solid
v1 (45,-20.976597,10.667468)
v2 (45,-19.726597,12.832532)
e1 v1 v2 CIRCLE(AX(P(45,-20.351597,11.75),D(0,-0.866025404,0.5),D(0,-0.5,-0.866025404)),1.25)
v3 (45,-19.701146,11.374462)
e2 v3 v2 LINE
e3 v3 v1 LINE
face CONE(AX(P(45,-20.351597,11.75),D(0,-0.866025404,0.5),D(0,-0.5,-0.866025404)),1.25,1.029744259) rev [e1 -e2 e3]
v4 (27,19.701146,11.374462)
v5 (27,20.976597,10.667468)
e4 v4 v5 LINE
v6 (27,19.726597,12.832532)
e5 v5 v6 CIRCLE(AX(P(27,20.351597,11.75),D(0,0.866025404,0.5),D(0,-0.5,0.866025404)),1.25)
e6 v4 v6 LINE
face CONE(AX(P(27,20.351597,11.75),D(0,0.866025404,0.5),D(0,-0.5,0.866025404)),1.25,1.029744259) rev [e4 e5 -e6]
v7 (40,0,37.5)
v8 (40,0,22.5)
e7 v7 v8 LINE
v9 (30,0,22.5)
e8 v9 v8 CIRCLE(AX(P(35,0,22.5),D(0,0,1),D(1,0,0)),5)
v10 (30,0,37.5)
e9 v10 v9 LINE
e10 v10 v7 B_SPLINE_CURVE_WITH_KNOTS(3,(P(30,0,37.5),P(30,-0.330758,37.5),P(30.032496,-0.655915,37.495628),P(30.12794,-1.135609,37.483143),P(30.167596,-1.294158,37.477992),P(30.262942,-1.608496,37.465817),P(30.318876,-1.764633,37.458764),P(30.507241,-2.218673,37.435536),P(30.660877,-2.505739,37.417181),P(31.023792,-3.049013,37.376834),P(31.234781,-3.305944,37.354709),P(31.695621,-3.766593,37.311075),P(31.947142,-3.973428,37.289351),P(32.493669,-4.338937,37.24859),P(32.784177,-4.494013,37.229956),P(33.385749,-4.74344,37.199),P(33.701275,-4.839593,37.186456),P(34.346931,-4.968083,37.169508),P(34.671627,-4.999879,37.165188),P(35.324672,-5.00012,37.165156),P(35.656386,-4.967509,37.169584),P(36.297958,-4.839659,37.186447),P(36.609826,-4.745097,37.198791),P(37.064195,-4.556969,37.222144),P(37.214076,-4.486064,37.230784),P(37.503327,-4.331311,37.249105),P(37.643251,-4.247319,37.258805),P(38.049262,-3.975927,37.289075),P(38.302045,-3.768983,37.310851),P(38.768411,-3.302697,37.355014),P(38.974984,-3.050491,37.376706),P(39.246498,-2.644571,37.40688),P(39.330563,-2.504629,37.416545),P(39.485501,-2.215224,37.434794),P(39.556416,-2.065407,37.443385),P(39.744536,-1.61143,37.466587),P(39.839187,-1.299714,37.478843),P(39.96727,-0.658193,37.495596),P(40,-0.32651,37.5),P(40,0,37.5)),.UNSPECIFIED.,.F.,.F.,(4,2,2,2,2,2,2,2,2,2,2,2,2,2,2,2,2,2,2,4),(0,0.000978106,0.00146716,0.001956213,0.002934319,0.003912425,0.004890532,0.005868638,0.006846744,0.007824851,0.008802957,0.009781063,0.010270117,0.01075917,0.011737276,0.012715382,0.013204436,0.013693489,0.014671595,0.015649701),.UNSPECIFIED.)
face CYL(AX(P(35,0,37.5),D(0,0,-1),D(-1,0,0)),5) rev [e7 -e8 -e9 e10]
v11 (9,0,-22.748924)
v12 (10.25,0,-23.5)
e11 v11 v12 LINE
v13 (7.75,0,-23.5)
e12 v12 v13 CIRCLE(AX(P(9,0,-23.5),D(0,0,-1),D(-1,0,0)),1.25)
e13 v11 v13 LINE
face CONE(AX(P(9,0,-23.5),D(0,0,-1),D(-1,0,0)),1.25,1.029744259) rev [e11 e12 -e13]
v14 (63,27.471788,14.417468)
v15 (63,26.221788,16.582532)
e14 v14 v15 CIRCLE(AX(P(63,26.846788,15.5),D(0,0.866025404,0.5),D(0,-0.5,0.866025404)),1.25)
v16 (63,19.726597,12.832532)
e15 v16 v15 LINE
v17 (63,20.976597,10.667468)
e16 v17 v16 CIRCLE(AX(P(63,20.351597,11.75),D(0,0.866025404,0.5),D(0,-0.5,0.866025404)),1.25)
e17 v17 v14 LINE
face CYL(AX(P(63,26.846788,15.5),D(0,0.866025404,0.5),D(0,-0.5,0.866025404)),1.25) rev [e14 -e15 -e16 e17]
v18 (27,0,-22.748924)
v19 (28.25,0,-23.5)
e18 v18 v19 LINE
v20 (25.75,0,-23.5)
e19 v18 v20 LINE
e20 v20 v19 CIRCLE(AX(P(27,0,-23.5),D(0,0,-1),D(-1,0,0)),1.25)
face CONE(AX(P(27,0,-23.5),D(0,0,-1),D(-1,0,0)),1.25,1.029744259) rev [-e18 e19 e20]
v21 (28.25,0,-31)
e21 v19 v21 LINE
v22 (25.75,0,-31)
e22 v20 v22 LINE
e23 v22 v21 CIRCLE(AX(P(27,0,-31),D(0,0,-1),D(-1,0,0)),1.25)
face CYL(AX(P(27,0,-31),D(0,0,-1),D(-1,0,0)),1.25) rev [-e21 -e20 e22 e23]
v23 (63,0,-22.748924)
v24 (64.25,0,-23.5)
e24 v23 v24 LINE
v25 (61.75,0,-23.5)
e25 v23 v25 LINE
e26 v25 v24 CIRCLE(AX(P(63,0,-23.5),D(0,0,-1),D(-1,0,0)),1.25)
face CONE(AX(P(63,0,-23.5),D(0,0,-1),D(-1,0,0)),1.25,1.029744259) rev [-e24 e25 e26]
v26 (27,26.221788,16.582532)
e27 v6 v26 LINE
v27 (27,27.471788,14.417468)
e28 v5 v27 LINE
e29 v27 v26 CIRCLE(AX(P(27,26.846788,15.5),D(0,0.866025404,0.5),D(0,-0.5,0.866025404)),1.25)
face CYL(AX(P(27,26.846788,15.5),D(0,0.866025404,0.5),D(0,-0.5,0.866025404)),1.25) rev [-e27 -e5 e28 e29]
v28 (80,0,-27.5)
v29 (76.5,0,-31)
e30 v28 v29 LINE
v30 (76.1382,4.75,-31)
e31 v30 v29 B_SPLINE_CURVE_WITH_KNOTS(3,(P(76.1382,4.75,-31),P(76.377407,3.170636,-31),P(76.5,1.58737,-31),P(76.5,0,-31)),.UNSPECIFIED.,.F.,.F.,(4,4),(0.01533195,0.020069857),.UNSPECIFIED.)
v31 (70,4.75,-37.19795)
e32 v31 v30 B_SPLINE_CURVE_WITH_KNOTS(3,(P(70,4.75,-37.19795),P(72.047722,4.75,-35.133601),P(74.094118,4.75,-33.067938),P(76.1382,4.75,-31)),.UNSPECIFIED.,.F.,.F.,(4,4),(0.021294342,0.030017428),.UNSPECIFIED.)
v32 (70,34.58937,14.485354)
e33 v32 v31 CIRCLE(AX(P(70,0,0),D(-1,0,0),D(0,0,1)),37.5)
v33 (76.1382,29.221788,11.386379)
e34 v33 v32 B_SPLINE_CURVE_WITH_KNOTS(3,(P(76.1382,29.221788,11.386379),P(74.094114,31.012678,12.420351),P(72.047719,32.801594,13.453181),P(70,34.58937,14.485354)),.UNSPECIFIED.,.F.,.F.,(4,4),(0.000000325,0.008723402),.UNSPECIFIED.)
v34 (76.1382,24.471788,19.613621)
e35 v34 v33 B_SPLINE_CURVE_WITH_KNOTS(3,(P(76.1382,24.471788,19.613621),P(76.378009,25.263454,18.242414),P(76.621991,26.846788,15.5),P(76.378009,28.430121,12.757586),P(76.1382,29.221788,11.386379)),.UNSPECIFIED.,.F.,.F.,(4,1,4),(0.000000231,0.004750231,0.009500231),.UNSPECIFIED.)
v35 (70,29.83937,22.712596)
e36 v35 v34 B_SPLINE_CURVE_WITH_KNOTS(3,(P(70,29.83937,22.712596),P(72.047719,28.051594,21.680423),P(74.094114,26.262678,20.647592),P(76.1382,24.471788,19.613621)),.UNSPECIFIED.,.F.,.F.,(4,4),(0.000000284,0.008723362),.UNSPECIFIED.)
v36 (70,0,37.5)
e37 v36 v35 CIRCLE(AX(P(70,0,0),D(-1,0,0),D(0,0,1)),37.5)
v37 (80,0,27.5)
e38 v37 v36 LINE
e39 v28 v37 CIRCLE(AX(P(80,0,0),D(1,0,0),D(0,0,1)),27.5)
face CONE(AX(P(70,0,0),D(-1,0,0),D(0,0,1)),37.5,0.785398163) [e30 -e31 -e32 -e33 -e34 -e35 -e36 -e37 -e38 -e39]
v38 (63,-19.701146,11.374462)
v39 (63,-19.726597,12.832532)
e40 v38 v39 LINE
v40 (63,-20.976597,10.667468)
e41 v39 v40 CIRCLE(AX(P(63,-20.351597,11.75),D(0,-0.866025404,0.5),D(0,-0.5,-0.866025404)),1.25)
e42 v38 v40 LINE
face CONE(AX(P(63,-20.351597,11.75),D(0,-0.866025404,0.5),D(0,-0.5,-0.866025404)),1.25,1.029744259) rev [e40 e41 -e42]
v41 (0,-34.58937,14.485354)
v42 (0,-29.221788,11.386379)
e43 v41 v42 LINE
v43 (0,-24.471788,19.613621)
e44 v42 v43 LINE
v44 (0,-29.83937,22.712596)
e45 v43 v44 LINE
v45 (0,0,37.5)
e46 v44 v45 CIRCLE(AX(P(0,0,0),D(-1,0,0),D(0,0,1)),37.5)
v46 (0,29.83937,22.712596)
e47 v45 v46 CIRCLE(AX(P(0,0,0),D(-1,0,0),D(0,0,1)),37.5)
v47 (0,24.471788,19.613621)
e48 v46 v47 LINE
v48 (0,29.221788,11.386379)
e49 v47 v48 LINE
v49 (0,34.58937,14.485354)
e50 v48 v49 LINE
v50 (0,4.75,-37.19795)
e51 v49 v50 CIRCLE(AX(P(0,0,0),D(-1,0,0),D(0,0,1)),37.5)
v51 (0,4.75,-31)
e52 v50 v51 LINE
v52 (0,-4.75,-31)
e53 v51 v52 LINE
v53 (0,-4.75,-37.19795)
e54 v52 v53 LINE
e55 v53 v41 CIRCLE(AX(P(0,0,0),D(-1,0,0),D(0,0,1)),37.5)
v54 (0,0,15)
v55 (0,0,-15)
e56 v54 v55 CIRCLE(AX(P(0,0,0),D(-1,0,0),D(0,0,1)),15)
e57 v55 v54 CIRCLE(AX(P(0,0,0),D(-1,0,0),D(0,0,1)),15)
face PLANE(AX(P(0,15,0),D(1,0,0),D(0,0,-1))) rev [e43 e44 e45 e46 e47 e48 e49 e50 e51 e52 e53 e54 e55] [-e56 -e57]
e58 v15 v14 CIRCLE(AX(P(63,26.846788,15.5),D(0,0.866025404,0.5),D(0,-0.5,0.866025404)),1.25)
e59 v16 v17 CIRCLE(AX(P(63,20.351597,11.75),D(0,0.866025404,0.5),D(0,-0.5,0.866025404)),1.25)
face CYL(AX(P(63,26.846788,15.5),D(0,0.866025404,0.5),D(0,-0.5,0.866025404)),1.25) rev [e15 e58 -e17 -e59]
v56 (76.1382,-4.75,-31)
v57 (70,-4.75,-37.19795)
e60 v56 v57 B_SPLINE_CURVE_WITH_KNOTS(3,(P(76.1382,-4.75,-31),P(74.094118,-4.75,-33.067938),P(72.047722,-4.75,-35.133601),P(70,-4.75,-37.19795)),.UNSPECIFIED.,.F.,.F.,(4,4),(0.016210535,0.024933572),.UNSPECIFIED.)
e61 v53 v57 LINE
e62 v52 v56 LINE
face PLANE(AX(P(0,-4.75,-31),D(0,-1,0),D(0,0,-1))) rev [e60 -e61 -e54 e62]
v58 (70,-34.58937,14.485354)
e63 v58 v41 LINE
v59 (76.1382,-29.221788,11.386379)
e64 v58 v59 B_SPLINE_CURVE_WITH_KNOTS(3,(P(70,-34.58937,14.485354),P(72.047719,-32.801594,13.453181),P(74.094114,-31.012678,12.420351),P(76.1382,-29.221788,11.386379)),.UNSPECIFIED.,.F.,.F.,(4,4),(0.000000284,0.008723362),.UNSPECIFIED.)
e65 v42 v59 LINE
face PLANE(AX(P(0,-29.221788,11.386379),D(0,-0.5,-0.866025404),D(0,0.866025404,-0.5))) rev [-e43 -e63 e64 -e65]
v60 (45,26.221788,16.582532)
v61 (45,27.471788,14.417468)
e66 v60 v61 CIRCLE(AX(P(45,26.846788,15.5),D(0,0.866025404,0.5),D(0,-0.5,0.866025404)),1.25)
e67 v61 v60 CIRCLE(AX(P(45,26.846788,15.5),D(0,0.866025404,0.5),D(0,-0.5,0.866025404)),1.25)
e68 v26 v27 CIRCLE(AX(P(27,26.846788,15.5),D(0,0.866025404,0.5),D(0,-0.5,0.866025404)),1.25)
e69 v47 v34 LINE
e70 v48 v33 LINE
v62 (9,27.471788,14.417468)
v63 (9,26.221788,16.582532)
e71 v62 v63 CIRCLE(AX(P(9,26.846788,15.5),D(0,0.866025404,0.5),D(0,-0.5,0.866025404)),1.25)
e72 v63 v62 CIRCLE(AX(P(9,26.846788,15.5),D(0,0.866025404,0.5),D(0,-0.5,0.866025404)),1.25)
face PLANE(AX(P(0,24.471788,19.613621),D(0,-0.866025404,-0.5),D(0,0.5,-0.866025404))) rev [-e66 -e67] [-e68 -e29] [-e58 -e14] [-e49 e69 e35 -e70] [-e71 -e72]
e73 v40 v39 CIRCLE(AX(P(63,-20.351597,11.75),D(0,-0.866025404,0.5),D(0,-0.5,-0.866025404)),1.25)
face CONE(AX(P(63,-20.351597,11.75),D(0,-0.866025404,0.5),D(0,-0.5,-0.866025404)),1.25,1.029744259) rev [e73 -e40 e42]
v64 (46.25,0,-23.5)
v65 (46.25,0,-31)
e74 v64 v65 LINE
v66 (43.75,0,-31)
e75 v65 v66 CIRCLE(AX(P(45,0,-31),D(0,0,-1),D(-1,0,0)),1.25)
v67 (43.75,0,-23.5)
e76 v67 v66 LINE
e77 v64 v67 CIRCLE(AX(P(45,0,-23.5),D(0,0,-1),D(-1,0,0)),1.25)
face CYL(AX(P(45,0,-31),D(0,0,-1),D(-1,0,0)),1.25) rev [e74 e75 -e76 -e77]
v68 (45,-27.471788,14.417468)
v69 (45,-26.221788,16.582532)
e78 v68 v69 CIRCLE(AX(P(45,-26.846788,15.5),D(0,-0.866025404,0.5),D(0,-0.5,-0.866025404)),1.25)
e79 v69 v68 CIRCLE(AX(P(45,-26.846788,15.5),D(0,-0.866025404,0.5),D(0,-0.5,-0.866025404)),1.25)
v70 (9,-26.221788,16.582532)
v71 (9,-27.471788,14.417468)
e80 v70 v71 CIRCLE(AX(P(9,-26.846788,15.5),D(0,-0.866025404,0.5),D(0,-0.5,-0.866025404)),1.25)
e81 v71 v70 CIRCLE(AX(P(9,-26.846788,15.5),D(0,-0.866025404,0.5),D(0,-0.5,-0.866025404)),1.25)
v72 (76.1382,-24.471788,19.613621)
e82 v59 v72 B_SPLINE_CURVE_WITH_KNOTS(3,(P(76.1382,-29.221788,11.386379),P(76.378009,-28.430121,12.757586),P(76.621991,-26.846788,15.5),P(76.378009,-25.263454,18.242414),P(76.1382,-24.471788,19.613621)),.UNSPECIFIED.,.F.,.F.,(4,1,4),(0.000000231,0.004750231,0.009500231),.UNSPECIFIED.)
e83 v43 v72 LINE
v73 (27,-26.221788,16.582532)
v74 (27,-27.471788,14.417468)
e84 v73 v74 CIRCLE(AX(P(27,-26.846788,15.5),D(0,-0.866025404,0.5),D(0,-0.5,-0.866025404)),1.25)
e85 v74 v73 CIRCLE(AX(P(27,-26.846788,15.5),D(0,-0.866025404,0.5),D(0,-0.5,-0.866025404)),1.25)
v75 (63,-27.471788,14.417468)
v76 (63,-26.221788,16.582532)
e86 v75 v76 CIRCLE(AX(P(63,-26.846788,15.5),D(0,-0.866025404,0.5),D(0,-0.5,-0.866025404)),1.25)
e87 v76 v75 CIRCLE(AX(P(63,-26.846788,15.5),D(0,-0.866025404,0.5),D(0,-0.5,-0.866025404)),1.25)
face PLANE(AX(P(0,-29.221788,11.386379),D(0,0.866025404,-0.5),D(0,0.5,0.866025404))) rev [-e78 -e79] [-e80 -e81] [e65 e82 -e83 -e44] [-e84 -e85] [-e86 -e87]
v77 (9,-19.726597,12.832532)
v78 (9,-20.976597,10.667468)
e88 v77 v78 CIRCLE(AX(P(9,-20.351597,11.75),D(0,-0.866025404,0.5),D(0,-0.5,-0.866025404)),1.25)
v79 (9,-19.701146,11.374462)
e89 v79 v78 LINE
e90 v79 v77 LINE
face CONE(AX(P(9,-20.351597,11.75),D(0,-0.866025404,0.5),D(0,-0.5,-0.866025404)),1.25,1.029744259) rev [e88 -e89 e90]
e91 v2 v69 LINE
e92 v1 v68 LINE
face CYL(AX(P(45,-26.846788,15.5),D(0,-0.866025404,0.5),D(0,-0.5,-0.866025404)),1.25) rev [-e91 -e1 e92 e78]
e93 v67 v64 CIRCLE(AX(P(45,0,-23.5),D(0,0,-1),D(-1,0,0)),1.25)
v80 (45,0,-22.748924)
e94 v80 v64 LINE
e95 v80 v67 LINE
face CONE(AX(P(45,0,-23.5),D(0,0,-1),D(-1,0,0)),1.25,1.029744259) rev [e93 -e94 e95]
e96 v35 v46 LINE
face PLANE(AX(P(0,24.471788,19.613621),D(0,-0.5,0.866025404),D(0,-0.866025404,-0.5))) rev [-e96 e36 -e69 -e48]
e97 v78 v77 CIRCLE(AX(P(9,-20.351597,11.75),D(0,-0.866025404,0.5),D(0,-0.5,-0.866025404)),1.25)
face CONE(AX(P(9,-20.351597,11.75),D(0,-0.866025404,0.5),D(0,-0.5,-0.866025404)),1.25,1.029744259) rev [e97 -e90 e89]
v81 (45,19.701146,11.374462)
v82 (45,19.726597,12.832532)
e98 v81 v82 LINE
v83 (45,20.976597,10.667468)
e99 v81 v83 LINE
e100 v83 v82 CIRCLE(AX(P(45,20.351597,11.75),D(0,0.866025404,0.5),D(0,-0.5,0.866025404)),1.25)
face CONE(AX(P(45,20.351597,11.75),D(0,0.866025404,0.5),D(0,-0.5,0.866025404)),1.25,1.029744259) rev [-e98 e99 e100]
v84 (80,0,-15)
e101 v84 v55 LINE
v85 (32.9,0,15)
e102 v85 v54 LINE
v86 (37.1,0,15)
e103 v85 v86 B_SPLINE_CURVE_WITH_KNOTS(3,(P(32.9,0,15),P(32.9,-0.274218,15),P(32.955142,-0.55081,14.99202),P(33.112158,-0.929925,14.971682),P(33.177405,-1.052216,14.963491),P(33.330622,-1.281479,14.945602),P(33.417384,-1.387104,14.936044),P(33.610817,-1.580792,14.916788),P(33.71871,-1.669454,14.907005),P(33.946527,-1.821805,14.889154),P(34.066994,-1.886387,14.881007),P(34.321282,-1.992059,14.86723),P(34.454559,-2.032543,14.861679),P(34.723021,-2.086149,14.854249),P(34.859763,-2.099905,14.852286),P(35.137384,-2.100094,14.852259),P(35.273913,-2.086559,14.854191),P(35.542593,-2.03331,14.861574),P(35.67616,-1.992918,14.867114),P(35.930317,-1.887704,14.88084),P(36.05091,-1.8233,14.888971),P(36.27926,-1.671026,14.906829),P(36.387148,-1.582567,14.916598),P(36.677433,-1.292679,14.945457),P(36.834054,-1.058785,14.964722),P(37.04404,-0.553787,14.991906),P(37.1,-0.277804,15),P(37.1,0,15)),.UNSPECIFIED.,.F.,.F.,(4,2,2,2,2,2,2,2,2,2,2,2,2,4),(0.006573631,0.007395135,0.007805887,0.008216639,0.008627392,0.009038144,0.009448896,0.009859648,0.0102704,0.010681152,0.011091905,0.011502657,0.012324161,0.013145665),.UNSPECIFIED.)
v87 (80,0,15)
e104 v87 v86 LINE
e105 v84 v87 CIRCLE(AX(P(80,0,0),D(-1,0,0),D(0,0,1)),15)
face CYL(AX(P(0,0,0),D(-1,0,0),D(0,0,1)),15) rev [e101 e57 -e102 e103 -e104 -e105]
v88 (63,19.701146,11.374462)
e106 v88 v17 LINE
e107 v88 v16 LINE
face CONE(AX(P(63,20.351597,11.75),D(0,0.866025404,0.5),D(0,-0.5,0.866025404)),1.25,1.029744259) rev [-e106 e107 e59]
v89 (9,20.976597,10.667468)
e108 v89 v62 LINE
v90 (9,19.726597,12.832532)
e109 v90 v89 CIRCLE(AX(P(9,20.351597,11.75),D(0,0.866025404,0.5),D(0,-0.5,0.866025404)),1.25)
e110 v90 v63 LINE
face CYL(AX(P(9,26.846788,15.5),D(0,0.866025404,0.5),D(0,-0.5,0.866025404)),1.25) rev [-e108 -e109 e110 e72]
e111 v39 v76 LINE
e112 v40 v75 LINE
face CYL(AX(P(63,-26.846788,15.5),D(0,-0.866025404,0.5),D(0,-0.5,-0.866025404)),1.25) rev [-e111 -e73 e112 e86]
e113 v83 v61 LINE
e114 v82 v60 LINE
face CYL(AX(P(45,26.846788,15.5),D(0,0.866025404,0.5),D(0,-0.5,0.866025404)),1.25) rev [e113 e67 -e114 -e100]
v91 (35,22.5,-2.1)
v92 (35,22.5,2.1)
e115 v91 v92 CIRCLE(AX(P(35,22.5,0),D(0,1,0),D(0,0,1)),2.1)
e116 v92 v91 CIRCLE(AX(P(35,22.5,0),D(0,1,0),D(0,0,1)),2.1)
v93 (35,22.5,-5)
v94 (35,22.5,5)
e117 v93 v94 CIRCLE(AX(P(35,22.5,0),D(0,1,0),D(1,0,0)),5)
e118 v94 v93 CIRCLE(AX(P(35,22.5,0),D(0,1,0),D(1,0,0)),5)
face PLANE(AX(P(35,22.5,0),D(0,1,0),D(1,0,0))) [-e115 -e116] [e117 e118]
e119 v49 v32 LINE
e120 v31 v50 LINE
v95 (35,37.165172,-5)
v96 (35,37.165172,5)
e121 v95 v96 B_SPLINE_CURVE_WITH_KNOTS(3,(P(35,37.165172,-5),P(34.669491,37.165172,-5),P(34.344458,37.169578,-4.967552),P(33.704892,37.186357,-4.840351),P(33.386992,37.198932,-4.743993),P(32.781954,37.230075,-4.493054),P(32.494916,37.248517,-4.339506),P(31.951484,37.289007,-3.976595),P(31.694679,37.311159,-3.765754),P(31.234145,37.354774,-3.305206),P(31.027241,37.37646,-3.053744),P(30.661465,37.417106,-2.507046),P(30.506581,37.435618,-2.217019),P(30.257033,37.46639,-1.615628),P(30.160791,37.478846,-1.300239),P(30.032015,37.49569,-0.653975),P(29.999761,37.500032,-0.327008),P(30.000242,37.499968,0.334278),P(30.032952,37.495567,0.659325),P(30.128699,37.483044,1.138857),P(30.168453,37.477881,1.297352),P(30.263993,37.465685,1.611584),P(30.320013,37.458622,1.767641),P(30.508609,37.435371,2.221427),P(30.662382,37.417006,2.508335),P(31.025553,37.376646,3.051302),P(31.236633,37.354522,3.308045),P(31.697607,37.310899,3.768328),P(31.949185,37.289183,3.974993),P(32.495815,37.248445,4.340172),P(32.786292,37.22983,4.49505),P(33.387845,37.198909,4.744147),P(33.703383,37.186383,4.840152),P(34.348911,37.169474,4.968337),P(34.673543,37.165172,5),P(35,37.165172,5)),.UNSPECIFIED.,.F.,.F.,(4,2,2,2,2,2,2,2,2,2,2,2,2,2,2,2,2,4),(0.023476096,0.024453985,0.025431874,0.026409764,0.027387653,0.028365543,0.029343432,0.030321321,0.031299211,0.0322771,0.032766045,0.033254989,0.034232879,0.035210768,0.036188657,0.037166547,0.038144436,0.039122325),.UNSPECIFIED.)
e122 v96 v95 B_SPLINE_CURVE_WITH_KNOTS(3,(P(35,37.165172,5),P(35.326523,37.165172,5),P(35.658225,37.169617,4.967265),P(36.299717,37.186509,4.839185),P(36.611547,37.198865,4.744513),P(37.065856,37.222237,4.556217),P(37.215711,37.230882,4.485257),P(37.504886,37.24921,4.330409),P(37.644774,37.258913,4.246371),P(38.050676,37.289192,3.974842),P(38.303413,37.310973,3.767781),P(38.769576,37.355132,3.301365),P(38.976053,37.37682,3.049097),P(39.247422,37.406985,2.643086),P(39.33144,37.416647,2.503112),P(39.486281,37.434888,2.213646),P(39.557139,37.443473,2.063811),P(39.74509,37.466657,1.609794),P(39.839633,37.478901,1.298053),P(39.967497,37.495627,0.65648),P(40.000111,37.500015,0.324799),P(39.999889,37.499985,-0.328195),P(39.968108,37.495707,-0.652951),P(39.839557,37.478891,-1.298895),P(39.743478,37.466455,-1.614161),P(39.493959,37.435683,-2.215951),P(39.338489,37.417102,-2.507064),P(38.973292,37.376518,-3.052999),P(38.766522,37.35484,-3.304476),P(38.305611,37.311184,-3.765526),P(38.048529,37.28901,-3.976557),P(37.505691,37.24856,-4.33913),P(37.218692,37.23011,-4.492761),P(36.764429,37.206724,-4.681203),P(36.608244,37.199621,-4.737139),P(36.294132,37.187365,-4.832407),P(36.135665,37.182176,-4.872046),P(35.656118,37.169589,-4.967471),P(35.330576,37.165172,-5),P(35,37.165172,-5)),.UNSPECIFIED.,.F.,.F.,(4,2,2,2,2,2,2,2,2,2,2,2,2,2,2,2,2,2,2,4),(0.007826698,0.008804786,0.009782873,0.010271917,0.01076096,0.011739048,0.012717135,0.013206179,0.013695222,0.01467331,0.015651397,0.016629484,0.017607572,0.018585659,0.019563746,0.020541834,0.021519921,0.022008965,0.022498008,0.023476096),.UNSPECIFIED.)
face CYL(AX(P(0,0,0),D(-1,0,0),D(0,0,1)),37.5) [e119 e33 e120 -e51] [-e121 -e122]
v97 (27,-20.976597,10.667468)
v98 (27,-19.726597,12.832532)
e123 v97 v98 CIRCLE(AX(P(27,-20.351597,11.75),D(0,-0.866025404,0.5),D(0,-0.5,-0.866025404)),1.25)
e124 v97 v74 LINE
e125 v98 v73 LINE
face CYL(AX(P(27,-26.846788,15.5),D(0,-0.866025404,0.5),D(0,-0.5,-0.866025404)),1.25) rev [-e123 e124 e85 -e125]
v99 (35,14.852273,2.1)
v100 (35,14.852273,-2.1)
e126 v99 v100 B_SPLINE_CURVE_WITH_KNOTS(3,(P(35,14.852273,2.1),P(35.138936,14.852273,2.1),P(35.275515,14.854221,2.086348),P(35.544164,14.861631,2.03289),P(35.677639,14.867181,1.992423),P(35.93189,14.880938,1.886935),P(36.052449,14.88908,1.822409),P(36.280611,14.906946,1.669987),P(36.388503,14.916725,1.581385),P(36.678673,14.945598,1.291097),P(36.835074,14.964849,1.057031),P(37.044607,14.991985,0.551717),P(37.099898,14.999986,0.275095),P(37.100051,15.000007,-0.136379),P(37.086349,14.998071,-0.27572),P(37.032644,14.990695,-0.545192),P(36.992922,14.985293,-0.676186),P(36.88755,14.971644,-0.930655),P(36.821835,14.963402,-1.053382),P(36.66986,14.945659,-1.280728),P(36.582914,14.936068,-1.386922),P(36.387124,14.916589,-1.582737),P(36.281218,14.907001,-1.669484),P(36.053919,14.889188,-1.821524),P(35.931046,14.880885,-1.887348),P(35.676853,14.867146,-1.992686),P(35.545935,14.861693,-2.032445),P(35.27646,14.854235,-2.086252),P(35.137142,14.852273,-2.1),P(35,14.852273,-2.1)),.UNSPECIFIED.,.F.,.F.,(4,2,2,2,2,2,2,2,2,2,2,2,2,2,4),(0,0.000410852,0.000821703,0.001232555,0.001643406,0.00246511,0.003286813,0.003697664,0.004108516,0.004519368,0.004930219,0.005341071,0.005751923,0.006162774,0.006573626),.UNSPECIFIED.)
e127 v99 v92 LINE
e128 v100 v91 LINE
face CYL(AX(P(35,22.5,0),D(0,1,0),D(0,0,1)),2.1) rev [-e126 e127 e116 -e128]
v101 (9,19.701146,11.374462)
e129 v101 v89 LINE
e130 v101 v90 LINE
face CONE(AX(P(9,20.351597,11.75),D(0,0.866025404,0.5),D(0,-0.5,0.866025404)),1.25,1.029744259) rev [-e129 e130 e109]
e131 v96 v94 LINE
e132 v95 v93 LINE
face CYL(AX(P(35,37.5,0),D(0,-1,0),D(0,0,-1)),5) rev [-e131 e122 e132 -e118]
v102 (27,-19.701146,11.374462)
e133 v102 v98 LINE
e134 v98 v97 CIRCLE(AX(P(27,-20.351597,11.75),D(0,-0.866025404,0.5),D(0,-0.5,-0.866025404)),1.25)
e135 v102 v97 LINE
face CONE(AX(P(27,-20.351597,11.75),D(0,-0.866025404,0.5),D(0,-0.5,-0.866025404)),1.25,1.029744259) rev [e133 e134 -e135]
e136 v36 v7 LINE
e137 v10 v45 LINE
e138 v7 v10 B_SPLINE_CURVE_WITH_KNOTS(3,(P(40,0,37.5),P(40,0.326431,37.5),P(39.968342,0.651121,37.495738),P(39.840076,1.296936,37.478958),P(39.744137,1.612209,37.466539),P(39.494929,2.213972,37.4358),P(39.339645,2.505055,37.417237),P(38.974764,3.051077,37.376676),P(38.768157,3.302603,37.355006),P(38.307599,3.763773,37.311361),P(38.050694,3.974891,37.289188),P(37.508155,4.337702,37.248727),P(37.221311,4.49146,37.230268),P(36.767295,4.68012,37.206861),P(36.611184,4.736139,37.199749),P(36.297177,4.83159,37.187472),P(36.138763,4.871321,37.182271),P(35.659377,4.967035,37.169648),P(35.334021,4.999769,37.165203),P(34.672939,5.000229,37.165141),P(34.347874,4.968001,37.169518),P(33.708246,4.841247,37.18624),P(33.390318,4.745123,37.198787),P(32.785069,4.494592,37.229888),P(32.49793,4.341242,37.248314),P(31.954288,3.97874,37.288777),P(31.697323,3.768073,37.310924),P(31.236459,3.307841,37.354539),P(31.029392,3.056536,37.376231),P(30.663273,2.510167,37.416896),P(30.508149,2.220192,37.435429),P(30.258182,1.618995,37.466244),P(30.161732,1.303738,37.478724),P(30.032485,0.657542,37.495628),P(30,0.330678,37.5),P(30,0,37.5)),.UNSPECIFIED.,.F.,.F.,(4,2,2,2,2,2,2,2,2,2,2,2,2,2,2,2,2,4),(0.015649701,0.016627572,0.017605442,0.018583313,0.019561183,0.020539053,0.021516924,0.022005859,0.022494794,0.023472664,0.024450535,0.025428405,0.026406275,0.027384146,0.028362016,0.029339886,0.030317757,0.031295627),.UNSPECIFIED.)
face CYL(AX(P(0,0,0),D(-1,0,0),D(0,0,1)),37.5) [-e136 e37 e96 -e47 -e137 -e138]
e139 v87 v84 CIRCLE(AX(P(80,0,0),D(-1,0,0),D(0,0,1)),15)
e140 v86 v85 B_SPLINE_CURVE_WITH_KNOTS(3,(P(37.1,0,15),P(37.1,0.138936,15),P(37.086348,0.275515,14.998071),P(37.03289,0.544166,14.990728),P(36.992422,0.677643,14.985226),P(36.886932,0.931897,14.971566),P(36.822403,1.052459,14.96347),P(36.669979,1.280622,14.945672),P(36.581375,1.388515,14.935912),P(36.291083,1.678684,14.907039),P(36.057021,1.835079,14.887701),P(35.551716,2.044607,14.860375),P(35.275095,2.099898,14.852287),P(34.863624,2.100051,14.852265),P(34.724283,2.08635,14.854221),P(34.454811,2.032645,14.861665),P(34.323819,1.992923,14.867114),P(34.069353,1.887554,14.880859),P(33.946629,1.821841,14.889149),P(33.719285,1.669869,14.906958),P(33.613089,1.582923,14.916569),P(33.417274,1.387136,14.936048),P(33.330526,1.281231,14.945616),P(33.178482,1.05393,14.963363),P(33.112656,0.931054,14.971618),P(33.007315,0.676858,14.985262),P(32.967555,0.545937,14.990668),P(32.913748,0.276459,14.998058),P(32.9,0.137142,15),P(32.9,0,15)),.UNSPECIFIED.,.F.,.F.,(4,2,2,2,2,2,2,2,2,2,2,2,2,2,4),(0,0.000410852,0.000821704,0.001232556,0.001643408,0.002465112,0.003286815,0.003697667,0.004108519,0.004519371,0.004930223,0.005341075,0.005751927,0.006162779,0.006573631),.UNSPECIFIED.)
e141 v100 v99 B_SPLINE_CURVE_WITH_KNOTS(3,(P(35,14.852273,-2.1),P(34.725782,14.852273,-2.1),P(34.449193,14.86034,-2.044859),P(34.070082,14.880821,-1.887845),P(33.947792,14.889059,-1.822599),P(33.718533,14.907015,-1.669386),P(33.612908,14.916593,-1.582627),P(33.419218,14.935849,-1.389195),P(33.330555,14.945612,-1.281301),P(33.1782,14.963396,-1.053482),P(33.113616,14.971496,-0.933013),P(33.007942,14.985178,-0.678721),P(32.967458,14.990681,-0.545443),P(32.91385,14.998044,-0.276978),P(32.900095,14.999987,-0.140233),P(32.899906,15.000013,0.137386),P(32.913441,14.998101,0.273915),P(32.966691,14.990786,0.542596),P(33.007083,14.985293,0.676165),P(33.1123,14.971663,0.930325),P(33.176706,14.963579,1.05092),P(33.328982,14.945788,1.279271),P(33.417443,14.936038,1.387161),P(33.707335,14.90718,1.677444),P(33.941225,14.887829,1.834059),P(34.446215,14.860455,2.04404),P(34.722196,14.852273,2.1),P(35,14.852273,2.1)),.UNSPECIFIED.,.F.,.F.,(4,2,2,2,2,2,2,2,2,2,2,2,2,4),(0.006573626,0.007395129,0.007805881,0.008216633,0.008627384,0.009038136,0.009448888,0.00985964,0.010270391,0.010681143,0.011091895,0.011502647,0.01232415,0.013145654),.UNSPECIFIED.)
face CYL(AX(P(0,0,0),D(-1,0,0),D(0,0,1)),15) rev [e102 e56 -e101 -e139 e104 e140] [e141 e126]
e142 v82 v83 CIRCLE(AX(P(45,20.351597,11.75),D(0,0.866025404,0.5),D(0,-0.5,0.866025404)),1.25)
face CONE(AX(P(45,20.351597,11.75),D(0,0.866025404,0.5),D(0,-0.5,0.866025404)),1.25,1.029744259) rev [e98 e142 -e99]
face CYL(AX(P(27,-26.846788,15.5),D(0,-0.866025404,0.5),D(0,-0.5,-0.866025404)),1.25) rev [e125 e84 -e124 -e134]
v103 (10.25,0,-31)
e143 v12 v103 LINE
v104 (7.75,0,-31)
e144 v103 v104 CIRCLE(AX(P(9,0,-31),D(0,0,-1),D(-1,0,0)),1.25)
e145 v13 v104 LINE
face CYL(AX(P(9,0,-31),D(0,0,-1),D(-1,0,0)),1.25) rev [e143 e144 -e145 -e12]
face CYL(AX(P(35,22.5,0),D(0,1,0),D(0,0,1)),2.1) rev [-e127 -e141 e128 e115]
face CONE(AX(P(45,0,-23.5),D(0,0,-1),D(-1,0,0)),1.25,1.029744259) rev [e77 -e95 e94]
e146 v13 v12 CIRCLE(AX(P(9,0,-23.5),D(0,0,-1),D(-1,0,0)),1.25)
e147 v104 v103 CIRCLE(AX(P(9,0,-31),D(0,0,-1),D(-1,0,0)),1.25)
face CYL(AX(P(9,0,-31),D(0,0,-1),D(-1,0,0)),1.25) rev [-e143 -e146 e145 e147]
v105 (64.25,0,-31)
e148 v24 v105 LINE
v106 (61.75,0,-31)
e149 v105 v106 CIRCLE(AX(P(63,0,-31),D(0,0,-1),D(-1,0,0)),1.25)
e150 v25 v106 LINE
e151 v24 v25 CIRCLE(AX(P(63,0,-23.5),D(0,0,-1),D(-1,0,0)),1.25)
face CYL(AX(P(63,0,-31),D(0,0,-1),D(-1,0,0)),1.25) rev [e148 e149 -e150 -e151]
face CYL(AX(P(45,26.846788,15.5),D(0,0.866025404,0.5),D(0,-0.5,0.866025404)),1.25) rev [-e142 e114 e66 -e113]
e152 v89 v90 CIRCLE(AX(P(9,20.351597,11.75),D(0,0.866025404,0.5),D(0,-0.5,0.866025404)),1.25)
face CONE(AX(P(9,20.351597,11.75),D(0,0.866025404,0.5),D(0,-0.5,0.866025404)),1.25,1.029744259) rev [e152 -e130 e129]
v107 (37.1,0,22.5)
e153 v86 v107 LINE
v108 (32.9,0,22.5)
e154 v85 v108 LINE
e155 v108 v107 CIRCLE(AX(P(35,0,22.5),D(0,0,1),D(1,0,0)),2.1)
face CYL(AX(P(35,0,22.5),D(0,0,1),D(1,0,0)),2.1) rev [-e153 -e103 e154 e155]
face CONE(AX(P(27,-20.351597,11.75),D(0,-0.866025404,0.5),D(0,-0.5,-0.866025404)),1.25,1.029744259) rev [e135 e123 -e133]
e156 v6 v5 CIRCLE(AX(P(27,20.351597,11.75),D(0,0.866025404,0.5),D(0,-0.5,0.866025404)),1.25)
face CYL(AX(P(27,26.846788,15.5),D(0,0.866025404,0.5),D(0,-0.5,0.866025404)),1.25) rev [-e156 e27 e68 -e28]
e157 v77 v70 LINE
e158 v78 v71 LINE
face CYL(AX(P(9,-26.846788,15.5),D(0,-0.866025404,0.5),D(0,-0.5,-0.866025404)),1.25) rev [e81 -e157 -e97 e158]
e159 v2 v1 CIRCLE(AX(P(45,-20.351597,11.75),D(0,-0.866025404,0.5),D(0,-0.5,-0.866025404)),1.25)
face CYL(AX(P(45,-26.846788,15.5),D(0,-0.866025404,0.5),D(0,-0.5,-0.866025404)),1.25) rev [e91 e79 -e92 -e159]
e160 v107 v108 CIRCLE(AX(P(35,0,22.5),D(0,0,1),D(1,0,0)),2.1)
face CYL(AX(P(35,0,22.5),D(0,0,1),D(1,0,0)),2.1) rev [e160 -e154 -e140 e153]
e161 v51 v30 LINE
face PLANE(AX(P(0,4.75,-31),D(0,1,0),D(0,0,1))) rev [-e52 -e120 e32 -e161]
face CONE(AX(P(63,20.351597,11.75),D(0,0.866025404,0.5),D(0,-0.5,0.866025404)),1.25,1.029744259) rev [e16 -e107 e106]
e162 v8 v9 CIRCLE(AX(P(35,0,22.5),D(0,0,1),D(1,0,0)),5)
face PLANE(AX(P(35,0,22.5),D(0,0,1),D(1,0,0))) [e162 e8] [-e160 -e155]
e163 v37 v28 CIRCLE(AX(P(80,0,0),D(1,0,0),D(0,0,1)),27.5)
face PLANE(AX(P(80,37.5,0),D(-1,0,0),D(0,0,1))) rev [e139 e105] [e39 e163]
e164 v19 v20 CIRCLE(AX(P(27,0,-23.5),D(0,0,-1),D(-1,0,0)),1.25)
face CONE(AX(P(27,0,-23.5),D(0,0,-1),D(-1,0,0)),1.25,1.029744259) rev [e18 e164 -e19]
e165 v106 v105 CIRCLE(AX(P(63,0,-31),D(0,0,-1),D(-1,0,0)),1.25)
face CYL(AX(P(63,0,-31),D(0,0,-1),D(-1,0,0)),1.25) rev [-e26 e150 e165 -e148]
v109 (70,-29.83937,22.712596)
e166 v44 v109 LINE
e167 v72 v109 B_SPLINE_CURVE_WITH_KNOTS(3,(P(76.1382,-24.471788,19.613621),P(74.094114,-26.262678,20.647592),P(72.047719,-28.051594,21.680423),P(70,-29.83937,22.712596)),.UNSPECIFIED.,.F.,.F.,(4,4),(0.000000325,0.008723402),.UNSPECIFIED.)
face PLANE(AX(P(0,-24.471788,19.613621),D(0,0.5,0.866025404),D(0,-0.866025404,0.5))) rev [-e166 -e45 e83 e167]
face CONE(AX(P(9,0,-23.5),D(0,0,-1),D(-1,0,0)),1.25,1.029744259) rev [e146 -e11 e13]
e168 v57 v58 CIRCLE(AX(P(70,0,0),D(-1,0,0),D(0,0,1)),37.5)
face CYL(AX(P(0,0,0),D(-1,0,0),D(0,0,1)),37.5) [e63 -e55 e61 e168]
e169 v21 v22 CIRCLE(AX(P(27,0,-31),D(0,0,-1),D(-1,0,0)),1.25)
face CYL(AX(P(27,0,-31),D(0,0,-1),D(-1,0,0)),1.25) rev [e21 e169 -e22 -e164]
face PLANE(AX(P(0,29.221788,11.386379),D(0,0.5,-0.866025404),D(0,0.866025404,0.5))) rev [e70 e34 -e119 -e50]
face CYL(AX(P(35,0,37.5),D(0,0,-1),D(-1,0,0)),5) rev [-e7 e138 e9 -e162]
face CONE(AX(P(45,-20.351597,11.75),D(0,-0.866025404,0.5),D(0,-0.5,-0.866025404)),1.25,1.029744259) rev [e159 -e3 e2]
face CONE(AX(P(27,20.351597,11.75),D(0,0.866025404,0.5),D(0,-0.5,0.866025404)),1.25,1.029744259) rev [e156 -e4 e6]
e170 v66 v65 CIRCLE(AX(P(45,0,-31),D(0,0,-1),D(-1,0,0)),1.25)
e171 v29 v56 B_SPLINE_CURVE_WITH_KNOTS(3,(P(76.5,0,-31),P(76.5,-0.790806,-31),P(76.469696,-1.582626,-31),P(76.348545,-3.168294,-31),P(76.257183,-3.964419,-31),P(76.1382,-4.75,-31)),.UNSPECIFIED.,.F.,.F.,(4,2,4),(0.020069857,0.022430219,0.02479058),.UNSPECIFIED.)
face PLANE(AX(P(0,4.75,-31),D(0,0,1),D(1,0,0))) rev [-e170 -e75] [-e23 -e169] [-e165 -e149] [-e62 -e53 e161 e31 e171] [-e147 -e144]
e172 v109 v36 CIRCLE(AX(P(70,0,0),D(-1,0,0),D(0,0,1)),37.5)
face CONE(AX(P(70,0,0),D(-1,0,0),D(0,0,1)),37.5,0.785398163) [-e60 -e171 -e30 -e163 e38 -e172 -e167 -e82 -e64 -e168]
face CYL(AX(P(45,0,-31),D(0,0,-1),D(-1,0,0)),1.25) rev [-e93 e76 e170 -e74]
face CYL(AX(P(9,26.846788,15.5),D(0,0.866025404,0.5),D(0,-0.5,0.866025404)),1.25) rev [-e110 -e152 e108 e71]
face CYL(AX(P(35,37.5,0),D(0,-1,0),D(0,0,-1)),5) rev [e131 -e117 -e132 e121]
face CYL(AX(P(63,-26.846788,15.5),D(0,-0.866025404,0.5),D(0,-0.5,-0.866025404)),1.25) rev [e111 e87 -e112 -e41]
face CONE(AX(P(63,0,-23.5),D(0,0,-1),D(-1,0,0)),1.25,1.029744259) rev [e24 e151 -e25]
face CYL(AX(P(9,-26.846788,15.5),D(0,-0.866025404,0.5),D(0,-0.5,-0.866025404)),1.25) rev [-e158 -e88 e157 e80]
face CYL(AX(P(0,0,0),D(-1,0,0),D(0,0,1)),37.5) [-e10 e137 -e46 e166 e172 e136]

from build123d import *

# Parameters (mm, degrees)
SKETCH1_W                  = 80
SKETCH1_H                  = 22.5
CHAMFER1_SIZE              = 10
CUT_EXTRUDE1_START         = 22.5
SKETCH2_R                  = 5
CUT_EXTRUDE1_DEPTH         = 74.481769102
CIRPATTERN1_COUNT          = 2
CIRPATTERN1_ANGLE          = 90
SKETCH5_W                  = 13
SKETCH5_H                  = 9.5
CUT_EXTRUDE2_DEPTH         = 96.981769264
M3_TAPPED_HOLE1_AT_2_COUNT = 2
M3_TAPPED_HOLE1_AT_2_PITCH = 18
M3_TAPPED_HOLE1_AT_3_COUNT = 2
M3_TAPPED_HOLE1_AT_3_PITCH = 18
M3_TAPPED_HOLE1_AT_4_COUNT = 2
M3_TAPPED_HOLE1_AT_4_PITCH = 36
CIRPATTERN2_COUNT          = 3


with BuildPart() as part:
    # Sketch1 → Revolve1 (revolve)
    with BuildSketch(Plane.XY, mode=Mode.PRIVATE) as revolve1_sk:
        with Locations((40, 26.25)):
            Rectangle(SKETCH1_W, SKETCH1_H)
    revolve(revolve1_sk.sketch.rotate(Axis((0, 0, 0), (1, 0, 0)), 90), axis=Axis((0, 0, 0), (1, 0, 0)))

    # Chamfer1
    chamfer1_edges = [part.edges().sort_by_distance(p)[0] for p in [
        (80, 0, -37.5),
    ]]
    chamfer(chamfer1_edges, length=CHAMFER1_SIZE)

    # Sketch2 → Cut-Extrude1 (cut, through all)
    with BuildSketch(Plane.XY.offset(CUT_EXTRUDE1_START)):
        with Locations((35, 0)):
            Circle(SKETCH2_R)
    cut_extrude1 = extrude(amount=CUT_EXTRUDE1_DEPTH, mode=Mode.SUBTRACT)

    # Sketch3 → M5 Tapped Hole1 (revolve, cut)
    with BuildSketch(Plane(origin=(35, 0, 22.5), x_dir=(0, -1, 0), z_dir=(1, 0, 0))):
        Polygon((0, 0), (0, 13.6618073), (2.1, 12.4), (2.1, 0), align=None)
    m5_tapped_hole1 = revolve(axis=Axis((35, 0, 28.85), (0, 0, -1)), mode=Mode.SUBTRACT)

    # CirPattern1: Cut-Extrude1, M5 Tapped Hole1 ×2 about axis
    cirpattern1_axis = Axis((0, 0, 0), (-1, 0, 0))
    add([cut_extrude1.rotate(cirpattern1_axis, i * CIRPATTERN1_ANGLE / (CIRPATTERN1_COUNT - 1)) for i in range(1, CIRPATTERN1_COUNT)], mode=Mode.SUBTRACT)
    add([m5_tapped_hole1.rotate(cirpattern1_axis, i * CIRPATTERN1_ANGLE / (CIRPATTERN1_COUNT - 1)) for i in range(1, CIRPATTERN1_COUNT)], mode=Mode.SUBTRACT)

    # Sketch5 → Cut-Extrude2 (cut, through all)
    with BuildSketch(Plane(origin=(80, 0, 0), x_dir=(0, 0, -1), z_dir=(1, 0, 0))):
        with Locations((37.5, 0)):
            Rectangle(SKETCH5_W, SKETCH5_H)
    cut_extrude2 = extrude(amount=-CUT_EXTRUDE2_DEPTH, mode=Mode.SUBTRACT)

    # Sketch6 → M3 Tapped Hole1 (revolve, cut)
    with BuildSketch(Plane(origin=(45, 0, -31), x_dir=(0, 1, 0), z_dir=(1, 0, 0))):
        Polygon((0, 0), (0, 8.251075774), (1.25, 7.5), (1.25, 0), align=None)
    m3_tapped_hole1 = revolve(axis=Axis((45, 0, -37.35), (0, 0, 1)), mode=Mode.SUBTRACT)

    # M3 Tapped Hole1 at 2: M3 Tapped Hole1 ×2
    with Locations(*[(i * M3_TAPPED_HOLE1_AT_2_PITCH, 0, 0) for i in range(1, M3_TAPPED_HOLE1_AT_2_COUNT)]):
        add(m3_tapped_hole1, mode=Mode.SUBTRACT)

    # M3 Tapped Hole1 at 3: M3 Tapped Hole1 ×2
    with Locations(*[(-i * M3_TAPPED_HOLE1_AT_3_PITCH, 0, 0) for i in range(1, M3_TAPPED_HOLE1_AT_3_COUNT)]):
        add(m3_tapped_hole1, mode=Mode.SUBTRACT)

    # M3 Tapped Hole1 at 4: M3 Tapped Hole1 ×2
    with Locations(*[(-i * M3_TAPPED_HOLE1_AT_4_PITCH, 0, 0) for i in range(1, M3_TAPPED_HOLE1_AT_4_COUNT)]):
        add(m3_tapped_hole1, mode=Mode.SUBTRACT)

    # CirPattern2: Cut-Extrude2, M3 Tapped Hole1 ×3 about axis
    cirpattern2_axis = Axis((0, 0, 0), (1, 0, 0))
    add([cut_extrude2.rotate(cirpattern2_axis, i * 360 / CIRPATTERN2_COUNT) for i in range(1, CIRPATTERN2_COUNT)], mode=Mode.SUBTRACT)
    add([m3_tapped_hole1.rotate(cirpattern2_axis, i * 360 / CIRPATTERN2_COUNT) for i in range(1, CIRPATTERN2_COUNT)], mode=Mode.SUBTRACT)

    # CirPattern2 copy 1 sketch → CirPattern2 copy 1 (revolve, cut)
    with BuildSketch(Plane(origin=(63, 26.846787517, 15.5), x_dir=(0, -0.4999999999999998, 0.8660254037844387), z_dir=(1, 0, 0))):
        Polygon((0, 0), (0, 8.251075774), (1.25, 7.5), (1.25, 0), align=None)
    revolve(axis=Axis((63, 32.346048831, 18.675), (0, -0.8660254037844387, -0.4999999999999998)), mode=Mode.SUBTRACT)

    # CirPattern2 copy 2 sketch → CirPattern2 copy 2 (revolve, cut)
    with BuildSketch(Plane(origin=(63, -26.846787517, 15.5), x_dir=(0, -0.5000000000000004, -0.8660254037844384), z_dir=(1, 0, 0))):
        Polygon((0, 0), (0, 8.251075774), (1.25, 7.5), (1.25, 0), align=None)
    revolve(axis=Axis((63, -32.346048831, 18.675), (0, 0.8660254037844384, -0.5000000000000004)), mode=Mode.SUBTRACT)

    # CirPattern2 copy 3 sketch → CirPattern2 copy 3 (revolve, cut)
    with BuildSketch(Plane(origin=(27, 26.846787517, 15.5), x_dir=(0, -0.4999999999999998, 0.8660254037844387), z_dir=(1, 0, 0))):
        Polygon((0, 0), (0, 8.251075774), (1.25, 7.5), (1.25, 0), align=None)
    revolve(axis=Axis((27, 32.346048831, 18.675), (0, -0.8660254037844387, -0.4999999999999998)), mode=Mode.SUBTRACT)

    # CirPattern2 copy 4 sketch → CirPattern2 copy 4 (revolve, cut)
    with BuildSketch(Plane(origin=(27, -26.846787517, 15.5), x_dir=(0, -0.5000000000000004, -0.8660254037844384), z_dir=(1, 0, 0))):
        Polygon((0, 0), (0, 8.251075774), (1.25, 7.5), (1.25, 0), align=None)
    revolve(axis=Axis((27, -32.346048831, 18.675), (0, 0.8660254037844384, -0.5000000000000004)), mode=Mode.SUBTRACT)

    # CirPattern2 copy 5 sketch → CirPattern2 copy 5 (revolve, cut)
    with BuildSketch(Plane(origin=(9, 26.846787517, 15.5), x_dir=(0, -0.4999999999999998, 0.8660254037844387), z_dir=(1, 0, 0))):
        Polygon((0, 0), (0, 8.251075774), (1.25, 7.5), (1.25, 0), align=None)
    revolve(axis=Axis((9, 32.346048831, 18.675), (0, -0.8660254037844387, -0.4999999999999998)), mode=Mode.SUBTRACT)

    # CirPattern2 copy 6 sketch → CirPattern2 copy 6 (revolve, cut)
    with BuildSketch(Plane(origin=(9, -26.846787517, 15.5), x_dir=(0, -0.5000000000000004, -0.8660254037844384), z_dir=(1, 0, 0))):
        Polygon((0, 0), (0, 8.251075774), (1.25, 7.5), (1.25, 0), align=None)
    revolve(axis=Axis((9, -32.346048831, 18.675), (0, 0.8660254037844384, -0.5000000000000004)), mode=Mode.SUBTRACT)


solid = part.part
